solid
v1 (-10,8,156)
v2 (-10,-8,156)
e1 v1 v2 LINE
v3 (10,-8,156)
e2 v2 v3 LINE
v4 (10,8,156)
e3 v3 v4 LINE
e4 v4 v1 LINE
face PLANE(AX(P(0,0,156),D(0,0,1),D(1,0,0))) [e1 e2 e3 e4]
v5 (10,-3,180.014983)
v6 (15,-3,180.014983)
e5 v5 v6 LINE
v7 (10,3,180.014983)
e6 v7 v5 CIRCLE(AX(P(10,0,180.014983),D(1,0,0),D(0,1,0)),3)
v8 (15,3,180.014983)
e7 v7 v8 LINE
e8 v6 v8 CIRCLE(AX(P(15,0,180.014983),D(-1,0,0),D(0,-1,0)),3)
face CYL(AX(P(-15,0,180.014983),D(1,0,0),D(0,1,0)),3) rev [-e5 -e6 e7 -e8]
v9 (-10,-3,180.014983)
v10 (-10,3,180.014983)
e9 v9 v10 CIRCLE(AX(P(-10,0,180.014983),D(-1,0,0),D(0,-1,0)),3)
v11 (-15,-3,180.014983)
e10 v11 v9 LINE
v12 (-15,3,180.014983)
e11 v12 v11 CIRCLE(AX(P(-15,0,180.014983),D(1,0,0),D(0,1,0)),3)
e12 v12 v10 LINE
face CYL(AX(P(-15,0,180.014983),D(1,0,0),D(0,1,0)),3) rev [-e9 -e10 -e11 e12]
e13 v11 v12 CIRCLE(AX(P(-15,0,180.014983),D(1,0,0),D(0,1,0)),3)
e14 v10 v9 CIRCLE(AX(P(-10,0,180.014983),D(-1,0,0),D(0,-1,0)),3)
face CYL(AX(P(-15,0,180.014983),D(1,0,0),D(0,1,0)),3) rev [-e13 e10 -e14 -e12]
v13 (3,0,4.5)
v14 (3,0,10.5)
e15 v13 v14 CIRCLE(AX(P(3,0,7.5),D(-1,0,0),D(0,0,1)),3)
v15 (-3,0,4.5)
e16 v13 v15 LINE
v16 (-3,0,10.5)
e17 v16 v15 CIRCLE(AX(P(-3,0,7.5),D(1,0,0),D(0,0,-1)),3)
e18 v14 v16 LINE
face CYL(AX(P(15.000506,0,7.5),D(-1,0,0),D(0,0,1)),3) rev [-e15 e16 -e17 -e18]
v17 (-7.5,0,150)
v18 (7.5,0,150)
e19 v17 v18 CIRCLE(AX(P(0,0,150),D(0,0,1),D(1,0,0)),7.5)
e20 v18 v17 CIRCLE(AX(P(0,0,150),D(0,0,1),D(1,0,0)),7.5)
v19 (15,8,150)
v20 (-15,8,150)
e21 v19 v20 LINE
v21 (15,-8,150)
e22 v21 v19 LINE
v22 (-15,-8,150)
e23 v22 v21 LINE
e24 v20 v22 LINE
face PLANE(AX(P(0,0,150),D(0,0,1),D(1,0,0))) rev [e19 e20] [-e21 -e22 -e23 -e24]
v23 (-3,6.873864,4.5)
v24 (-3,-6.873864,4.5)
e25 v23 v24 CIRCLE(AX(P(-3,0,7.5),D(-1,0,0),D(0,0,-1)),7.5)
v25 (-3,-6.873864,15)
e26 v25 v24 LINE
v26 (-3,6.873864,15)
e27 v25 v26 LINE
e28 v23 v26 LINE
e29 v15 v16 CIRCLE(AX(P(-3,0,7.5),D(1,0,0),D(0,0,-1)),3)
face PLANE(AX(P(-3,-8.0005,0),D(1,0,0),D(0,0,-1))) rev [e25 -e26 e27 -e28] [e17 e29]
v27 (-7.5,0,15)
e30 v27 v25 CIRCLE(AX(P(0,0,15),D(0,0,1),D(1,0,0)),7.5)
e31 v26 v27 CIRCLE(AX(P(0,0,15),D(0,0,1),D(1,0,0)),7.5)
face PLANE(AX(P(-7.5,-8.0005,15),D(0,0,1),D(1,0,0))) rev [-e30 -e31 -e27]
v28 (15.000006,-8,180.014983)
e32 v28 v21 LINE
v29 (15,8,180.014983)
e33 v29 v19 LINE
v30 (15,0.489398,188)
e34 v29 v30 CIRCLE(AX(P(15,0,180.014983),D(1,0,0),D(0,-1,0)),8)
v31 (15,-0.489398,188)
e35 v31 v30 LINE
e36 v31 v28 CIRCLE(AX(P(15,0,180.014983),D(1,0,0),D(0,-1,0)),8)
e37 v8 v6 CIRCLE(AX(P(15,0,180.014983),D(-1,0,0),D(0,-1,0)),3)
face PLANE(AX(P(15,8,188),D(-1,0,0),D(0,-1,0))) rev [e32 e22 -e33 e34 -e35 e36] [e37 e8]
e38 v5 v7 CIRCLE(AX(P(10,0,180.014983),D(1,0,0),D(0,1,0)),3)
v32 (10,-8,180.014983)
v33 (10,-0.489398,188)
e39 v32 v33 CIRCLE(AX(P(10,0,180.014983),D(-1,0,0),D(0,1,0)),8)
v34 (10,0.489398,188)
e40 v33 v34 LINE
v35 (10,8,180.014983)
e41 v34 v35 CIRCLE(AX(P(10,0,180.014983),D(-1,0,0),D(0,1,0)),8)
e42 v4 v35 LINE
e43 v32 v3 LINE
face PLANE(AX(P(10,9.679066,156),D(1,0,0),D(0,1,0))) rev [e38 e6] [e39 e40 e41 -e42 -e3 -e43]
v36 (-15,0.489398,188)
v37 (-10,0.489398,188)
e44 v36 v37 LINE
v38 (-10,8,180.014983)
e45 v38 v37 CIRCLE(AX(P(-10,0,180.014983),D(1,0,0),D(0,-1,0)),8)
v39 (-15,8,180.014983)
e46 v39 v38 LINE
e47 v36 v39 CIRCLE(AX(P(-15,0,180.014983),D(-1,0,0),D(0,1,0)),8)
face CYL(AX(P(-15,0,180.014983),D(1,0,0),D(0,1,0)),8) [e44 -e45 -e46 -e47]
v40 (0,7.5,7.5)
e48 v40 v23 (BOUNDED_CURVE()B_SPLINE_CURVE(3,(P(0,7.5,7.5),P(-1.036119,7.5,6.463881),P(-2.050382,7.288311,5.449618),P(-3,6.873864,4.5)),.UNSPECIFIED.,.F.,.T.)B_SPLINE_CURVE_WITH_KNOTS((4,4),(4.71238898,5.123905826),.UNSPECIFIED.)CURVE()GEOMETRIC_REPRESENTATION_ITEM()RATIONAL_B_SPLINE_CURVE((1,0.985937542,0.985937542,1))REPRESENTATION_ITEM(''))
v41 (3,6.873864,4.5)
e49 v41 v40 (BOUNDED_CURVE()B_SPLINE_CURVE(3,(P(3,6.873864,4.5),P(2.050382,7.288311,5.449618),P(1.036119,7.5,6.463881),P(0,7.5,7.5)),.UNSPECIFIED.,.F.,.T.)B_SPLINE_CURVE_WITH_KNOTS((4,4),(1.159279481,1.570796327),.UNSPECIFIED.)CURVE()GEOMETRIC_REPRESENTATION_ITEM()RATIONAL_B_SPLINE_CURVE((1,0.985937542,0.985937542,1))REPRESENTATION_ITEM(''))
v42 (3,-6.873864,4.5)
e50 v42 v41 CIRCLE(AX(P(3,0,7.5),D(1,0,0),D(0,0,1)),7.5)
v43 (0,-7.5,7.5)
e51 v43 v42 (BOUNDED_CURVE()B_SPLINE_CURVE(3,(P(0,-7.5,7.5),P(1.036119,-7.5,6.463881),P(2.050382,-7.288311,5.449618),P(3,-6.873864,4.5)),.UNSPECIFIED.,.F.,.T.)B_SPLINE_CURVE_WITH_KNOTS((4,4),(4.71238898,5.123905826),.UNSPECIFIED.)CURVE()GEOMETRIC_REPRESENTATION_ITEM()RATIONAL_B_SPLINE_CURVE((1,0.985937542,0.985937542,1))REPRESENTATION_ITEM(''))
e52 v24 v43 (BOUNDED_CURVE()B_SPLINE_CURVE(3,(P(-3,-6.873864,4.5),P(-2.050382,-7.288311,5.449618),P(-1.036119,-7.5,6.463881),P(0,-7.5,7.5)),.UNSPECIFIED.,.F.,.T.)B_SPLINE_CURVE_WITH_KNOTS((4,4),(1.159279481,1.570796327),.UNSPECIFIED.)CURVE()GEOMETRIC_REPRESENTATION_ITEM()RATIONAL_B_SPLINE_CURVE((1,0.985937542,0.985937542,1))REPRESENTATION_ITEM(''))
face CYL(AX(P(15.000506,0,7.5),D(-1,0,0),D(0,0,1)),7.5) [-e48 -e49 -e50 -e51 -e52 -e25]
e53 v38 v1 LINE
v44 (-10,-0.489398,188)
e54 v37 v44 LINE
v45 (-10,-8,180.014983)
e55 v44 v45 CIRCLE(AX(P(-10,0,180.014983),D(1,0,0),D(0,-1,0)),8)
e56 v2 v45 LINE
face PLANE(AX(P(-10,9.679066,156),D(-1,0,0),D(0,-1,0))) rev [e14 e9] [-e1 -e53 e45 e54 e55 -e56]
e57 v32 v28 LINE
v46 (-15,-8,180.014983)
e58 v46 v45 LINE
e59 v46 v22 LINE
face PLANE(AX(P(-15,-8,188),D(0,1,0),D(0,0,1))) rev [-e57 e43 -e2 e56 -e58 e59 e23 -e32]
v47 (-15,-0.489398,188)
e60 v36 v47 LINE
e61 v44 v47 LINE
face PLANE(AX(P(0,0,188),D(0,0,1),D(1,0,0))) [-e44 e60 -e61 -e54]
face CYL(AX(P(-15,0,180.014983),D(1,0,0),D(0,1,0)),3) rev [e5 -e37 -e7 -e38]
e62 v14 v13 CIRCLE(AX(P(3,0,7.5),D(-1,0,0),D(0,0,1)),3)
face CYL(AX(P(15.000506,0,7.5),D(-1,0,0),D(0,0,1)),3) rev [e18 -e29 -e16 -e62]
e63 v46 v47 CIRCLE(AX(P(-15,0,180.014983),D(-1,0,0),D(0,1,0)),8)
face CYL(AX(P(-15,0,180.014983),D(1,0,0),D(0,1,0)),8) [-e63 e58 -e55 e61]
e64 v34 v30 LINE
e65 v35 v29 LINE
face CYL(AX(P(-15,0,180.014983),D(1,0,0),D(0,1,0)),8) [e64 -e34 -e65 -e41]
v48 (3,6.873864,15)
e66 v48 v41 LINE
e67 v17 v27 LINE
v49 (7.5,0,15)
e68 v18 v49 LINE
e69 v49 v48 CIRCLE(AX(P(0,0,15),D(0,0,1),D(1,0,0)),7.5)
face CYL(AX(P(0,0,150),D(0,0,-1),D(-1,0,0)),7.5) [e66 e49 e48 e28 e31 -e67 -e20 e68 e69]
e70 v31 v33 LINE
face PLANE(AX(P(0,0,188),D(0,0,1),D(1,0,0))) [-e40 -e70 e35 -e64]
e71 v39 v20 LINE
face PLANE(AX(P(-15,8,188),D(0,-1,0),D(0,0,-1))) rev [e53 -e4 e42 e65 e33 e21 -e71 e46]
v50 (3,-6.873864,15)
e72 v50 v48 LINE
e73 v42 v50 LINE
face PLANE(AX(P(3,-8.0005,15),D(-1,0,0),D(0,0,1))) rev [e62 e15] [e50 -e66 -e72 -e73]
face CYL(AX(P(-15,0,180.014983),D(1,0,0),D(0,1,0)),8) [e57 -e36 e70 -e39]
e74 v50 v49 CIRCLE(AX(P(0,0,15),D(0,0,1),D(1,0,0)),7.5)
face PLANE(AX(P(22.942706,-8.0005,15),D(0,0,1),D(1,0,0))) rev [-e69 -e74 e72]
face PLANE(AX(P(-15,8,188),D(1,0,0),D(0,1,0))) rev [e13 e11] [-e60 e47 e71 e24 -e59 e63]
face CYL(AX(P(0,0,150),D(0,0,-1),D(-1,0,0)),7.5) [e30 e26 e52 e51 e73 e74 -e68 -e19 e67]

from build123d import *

# Parameters (mm, degrees)
SKETCH1_R               = 7.5
BOSS_EXTRUDE1_DEPTH     = 150
SKETCH2_W               = 30
SKETCH2_H               = 16
BOSS_EXTRUDE2_DEPTH     = 38
SKETCH3_W               = 20
SKETCH3_H               = 19.358131828
CUT_EXTRUDE1_DEPTH      = 32
CUT_EXTRUDE2_DEPTH      = 191.546582231
CUT_EXTRUDE2_DEPTH_BACK = 191.546582231
SKETCH4_R               = 3
CUT_EXTRUDE3_DEPTH      = 189.76705221
CUT_EXTRUDE3_DEPTH_BACK = 189.76705221
SKETCH5_W               = 4.5
SKETCH5_H               = 15
SKETCH5_W_2             = 19.942706309
CUT_EXTRUDE4_DEPTH      = 190.029098289
CUT_EXTRUDE4_DEPTH_BACK = 190.029098289
SKETCH6_R               = 3


with BuildPart() as part:
    # Sketch1 → Boss-Extrude1 (new body)
    with BuildSketch(Plane.XY):
        Circle(SKETCH1_R)
    extrude(amount=BOSS_EXTRUDE1_DEPTH)

    # Sketch2 → Boss-Extrude2 (add)
    with BuildSketch(Plane.XY.offset(150)):
        Rectangle(SKETCH2_W, SKETCH2_H)
    extrude(amount=BOSS_EXTRUDE2_DEPTH)

    # Sketch3 → Cut-Extrude1 (cut)
    with BuildSketch(Plane.XY.offset(188)):
        Rectangle(SKETCH3_W, SKETCH3_H)
    extrude(amount=-CUT_EXTRUDE1_DEPTH, mode=Mode.SUBTRACT)

    # Sketch4 → Cut-Extrude2 (cut, two sides: drawn at the far end of the back side and taken through both)
    with BuildSketch(Plane(origin=(15, 0, 0), x_dir=(0, 0, -1), z_dir=(1, 0, 0)).offset(-CUT_EXTRUDE2_DEPTH_BACK)):
        with Locations(Location((-180.014983451, 0, 0), (0, 0, 90))):
            Circle(SKETCH4_R)
        with BuildLine():
            Line((-180.014983451, 8), (-180.014983451, 17.706818894))
            Line((-180.014983451, 17.706818894), (-220.326825599, 17.706818894))
            Line((-220.326825599, 17.706818894), (-218.614105417, -20.299257523))
            Line((-218.614105417, -20.299257523), (-180.014983451, -8))
            ThreePointArc((-180.014983451, -8), (-188.014983451, 0), (-180.014983451, 8))
        make_face()
    extrude(amount=CUT_EXTRUDE2_DEPTH + CUT_EXTRUDE2_DEPTH_BACK, mode=Mode.SUBTRACT)

    # Sketch5 → Cut-Extrude3 (cut, two sides: drawn at the far end of the back side and taken through both)
    with BuildSketch(Plane(origin=(0, 0, 0), x_dir=(1, 0, 0), z_dir=(0, 1, 0)).offset(-CUT_EXTRUDE3_DEPTH_BACK)):
        with Locations((-5.25, -7.5)):
            Rectangle(SKETCH5_W, SKETCH5_H)
        with Locations((12.971353155, -7.5)):
            Rectangle(SKETCH5_W_2, SKETCH5_H)
    extrude(amount=CUT_EXTRUDE3_DEPTH + CUT_EXTRUDE3_DEPTH_BACK, mode=Mode.SUBTRACT)

    # Sketch6 → Cut-Extrude4 (cut, two sides: drawn at the far end of the back side and taken through both)
    with BuildSketch(Plane.ZY.offset(3).offset(-CUT_EXTRUDE4_DEPTH_BACK)):
        with Locations((7.5, 0)):
            Circle(SKETCH6_R)
        with BuildLine():
            Line((7.5, 7.5), (-1.727121044, 19.130973882))
            Line((-1.727121044, 19.130973882), (-13.960832092, -5.232772696))
            Line((-13.960832092, -5.232772696), (1.279468959, -23.272312715))
            Line((1.279468959, -23.272312715), (7.5, -7.5))
            ThreePointArc((7.5, -7.5), (0, 0), (7.5, 7.5))
        make_face()
    extrude(amount=CUT_EXTRUDE4_DEPTH + CUT_EXTRUDE4_DEPTH_BACK, mode=Mode.SUBTRACT)


solid = part.part
